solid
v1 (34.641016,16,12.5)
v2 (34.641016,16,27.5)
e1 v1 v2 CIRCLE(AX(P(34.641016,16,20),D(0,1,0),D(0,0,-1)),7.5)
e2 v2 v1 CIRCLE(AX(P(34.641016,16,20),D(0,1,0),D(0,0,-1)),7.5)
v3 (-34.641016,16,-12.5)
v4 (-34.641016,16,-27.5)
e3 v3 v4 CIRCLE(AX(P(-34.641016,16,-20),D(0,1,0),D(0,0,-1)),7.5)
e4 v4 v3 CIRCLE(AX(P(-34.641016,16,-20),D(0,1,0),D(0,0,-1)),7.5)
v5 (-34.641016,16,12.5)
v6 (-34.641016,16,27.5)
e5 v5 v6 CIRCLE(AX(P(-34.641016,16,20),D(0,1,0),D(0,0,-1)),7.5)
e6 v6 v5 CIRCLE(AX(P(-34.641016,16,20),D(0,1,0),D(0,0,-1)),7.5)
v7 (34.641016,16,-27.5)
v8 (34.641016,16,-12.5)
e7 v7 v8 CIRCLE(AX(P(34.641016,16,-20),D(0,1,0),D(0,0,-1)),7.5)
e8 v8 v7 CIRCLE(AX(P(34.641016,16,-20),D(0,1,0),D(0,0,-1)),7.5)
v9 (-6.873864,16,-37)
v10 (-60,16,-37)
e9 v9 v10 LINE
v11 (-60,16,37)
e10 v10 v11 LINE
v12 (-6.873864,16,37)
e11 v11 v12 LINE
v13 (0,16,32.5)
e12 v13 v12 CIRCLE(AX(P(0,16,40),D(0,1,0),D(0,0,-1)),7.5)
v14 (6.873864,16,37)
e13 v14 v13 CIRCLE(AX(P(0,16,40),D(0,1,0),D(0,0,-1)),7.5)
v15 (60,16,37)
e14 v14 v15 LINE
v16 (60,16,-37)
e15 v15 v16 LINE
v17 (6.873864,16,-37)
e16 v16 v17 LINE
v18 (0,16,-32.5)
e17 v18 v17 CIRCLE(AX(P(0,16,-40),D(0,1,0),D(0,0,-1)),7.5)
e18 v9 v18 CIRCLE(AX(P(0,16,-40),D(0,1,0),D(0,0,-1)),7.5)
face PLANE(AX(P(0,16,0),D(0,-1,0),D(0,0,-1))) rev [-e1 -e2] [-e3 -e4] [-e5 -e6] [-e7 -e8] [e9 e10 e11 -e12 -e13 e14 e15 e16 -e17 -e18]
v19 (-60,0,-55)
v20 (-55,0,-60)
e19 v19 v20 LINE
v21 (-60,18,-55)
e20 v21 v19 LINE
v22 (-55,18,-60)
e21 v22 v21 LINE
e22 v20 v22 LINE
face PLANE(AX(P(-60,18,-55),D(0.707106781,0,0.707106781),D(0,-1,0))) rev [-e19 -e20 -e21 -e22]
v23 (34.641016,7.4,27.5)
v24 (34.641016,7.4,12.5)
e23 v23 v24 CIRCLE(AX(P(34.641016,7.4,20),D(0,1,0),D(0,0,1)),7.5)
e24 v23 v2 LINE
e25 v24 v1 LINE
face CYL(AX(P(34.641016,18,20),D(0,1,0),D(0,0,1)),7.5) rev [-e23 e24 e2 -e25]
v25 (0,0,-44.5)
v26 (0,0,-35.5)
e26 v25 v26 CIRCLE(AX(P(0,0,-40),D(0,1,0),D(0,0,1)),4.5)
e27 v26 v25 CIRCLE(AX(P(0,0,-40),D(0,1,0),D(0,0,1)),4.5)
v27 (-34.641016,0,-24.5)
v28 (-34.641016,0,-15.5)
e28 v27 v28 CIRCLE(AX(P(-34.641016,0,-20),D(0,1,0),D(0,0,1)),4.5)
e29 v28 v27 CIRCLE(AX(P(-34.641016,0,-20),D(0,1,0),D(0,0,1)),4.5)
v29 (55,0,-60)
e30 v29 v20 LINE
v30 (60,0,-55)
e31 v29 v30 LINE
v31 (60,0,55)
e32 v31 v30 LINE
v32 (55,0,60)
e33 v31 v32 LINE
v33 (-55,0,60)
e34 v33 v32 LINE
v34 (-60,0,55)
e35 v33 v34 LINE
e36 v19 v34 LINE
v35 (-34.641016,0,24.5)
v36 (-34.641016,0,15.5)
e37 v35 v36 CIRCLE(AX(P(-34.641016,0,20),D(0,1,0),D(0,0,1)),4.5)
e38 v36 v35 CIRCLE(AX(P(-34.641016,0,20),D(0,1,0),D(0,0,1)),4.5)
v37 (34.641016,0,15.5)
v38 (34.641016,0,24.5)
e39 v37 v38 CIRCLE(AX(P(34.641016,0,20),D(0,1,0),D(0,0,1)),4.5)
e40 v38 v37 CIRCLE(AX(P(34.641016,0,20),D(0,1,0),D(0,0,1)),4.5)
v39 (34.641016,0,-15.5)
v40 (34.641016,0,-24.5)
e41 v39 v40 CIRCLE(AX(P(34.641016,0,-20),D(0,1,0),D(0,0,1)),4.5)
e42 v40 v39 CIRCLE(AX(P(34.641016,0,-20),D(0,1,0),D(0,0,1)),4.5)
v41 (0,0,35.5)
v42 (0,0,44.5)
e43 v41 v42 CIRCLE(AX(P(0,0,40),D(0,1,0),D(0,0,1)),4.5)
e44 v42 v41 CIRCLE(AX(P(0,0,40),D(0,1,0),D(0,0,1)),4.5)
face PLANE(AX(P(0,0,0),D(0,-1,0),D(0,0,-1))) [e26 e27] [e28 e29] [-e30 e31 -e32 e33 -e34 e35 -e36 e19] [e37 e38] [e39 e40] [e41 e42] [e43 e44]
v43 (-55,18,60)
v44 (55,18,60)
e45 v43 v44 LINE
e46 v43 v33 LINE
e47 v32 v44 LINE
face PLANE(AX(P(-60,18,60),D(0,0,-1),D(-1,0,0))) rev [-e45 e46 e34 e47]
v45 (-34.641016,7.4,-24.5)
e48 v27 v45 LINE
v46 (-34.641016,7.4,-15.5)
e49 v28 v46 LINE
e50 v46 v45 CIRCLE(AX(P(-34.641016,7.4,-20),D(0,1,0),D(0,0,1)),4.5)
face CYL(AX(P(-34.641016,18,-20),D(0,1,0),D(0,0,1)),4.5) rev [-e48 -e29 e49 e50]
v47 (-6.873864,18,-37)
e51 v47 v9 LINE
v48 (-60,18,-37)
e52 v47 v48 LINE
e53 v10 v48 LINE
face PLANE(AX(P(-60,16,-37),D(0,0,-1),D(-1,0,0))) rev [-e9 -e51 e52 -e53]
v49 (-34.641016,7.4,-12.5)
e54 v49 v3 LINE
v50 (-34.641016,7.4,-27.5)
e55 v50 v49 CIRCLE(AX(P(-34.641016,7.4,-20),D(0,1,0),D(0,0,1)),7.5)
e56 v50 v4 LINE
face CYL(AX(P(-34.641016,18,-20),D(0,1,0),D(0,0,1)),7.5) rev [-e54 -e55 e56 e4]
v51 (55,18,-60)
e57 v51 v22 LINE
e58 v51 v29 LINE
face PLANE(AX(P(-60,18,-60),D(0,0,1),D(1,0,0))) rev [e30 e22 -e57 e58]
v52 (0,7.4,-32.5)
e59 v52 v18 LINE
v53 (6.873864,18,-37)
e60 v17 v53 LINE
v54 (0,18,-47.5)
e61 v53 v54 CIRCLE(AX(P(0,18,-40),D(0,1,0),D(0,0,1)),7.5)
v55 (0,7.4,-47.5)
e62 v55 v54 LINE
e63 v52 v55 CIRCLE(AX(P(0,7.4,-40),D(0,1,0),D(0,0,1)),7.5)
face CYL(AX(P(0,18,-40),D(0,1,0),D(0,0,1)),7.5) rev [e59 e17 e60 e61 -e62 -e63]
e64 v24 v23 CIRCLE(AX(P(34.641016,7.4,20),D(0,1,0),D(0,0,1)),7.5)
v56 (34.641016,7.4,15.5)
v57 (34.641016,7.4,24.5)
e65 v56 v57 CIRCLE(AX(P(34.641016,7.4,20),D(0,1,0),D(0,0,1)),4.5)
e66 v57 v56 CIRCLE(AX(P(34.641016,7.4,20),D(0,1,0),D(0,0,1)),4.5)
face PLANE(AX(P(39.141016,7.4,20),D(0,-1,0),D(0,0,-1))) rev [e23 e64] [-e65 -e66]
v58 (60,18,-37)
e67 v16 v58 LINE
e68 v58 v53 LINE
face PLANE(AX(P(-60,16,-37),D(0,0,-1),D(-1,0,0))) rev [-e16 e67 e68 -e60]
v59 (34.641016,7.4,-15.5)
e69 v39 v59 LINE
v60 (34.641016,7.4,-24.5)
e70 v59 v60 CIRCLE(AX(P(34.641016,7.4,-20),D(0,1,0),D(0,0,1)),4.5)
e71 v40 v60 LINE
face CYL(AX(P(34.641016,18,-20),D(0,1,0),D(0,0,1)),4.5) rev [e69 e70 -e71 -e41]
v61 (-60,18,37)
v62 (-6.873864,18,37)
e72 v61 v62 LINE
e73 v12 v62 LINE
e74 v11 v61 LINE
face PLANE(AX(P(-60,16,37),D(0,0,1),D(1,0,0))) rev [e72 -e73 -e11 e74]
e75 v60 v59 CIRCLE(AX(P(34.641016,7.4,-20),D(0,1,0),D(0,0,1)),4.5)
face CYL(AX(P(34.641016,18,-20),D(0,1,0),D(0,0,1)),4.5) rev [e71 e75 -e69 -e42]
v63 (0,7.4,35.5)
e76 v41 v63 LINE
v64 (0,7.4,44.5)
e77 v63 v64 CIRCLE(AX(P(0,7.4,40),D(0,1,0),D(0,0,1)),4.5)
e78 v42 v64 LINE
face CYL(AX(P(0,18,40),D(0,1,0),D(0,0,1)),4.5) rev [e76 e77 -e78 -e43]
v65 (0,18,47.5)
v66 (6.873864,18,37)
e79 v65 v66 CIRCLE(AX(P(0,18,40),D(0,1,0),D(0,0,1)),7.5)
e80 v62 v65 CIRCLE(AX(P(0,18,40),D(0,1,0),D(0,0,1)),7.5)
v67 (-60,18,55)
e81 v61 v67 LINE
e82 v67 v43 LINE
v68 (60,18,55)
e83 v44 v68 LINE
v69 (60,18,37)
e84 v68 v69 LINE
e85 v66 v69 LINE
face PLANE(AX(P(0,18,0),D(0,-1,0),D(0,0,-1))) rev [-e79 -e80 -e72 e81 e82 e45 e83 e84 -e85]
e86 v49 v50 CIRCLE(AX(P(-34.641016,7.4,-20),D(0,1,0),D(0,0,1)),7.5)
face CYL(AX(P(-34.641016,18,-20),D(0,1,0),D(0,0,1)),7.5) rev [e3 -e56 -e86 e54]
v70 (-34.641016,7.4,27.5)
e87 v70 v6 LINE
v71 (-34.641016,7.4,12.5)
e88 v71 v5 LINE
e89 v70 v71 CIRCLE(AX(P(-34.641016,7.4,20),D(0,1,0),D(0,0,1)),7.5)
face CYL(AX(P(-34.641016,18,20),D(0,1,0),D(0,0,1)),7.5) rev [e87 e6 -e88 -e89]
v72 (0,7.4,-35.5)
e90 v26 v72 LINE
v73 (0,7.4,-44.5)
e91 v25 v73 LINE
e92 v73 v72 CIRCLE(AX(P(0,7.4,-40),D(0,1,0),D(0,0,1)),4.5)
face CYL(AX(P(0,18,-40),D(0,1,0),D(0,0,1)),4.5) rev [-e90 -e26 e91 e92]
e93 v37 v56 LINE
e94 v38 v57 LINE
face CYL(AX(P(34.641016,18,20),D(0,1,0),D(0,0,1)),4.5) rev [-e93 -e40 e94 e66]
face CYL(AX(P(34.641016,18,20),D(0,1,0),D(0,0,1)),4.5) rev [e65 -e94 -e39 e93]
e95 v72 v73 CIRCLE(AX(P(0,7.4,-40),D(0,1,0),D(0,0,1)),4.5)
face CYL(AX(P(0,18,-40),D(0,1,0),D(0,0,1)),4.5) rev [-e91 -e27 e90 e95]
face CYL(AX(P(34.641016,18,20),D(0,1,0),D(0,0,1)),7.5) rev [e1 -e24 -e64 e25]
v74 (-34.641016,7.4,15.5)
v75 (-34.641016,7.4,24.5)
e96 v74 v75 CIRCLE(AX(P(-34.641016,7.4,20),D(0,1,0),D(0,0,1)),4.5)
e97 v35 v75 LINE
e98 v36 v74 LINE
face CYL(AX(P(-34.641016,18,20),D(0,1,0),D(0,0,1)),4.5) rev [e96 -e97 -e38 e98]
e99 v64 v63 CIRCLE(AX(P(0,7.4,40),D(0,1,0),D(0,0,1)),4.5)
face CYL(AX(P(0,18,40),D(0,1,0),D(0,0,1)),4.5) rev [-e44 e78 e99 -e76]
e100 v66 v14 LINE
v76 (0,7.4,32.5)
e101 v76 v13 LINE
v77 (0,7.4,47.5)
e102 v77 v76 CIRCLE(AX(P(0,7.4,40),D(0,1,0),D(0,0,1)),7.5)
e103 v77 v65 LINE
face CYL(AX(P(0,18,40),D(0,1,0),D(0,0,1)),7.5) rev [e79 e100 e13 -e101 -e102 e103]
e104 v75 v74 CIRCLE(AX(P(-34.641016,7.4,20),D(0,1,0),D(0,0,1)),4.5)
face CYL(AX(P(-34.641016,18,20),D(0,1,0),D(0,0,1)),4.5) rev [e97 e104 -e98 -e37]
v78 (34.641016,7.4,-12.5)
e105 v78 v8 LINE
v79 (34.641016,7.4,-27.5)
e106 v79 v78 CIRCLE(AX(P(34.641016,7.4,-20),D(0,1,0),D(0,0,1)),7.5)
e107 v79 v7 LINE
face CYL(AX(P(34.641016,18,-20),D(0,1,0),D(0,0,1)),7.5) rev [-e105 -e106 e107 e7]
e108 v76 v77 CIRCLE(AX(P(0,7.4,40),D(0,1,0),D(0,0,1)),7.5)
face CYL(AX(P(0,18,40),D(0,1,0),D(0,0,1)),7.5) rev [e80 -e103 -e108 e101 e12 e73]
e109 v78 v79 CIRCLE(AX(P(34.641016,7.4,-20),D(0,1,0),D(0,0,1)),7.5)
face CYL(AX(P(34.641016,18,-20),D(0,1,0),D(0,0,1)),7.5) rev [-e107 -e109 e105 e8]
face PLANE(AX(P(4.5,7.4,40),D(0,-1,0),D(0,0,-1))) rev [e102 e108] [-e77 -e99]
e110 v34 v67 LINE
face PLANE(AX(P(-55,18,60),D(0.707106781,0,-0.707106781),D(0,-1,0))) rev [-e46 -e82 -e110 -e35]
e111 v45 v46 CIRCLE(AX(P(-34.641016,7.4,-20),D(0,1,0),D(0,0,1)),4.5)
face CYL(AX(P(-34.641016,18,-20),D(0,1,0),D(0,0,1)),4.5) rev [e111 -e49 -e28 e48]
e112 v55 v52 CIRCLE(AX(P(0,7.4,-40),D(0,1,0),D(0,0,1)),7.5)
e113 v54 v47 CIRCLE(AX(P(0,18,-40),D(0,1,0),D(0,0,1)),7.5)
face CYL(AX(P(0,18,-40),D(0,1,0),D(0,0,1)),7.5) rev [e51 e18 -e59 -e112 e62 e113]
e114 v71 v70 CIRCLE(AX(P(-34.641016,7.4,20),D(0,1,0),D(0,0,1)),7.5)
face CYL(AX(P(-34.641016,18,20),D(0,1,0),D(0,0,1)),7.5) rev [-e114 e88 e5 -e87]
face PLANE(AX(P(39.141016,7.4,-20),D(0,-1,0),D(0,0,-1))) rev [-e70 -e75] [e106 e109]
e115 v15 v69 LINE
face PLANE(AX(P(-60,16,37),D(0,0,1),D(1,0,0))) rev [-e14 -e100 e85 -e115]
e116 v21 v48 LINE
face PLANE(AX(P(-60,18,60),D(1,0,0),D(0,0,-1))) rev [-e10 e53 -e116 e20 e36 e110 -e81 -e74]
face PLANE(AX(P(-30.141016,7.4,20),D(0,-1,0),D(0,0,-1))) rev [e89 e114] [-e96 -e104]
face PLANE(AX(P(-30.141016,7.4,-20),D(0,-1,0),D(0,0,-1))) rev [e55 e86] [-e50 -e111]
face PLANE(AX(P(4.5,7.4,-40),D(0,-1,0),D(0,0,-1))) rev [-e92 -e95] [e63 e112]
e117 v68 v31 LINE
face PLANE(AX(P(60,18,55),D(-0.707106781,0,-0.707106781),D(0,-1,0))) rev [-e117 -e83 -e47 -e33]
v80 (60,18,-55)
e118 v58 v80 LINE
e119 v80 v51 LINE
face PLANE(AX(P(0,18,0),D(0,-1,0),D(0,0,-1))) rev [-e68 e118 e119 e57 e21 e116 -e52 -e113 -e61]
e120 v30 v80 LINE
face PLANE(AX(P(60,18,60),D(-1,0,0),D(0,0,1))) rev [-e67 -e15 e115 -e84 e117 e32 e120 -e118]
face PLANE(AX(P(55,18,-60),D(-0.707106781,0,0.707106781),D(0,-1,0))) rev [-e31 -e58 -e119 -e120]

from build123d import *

# Parameters (mm, degrees)
SKETCH_1_W                   = 120
SKETCH_1_H                   = 120
EXTRUDE_1_DEPTH              = 18
HOLE_WIZARD_M8_3_D           = 9
HOLE_WIZARD_M8_3_CBORE_D     = 15
HOLE_WIZARD_M8_3_CBORE_DEPTH = 10.6
SKETCH_11_W                  = 120
SKETCH_11_H                  = 74
CUT_EXTRUDE_2_DEPTH          = 2
CHAMFER_1_SIZE               = 5


with BuildPart() as part:
    # 草图1 → 凸台-拉伸1 (new body)
    with BuildSketch(Plane(origin=(0, 0, 0), x_dir=(1, 0, 0), z_dir=(0, 1, 0))):
        Rectangle(SKETCH_1_W, SKETCH_1_H)
    extrude(amount=EXTRUDE_1_DEPTH)

    # M8 六角凹头螺钉的柱形沉头孔3 (through all)
    with Locations(Plane(origin=(0, 18, 0), x_dir=(1, 0, 0), z_dir=(0, 1, 0))):
        with Locations((0, 40), (-34.641016151, 20), (-34.641016151, -20), (0, -40), (34.641016151, -20), (34.641016151, 20)):
            CounterBoreHole(HOLE_WIZARD_M8_3_D / 2, HOLE_WIZARD_M8_3_CBORE_D / 2, HOLE_WIZARD_M8_3_CBORE_DEPTH)

    # 草图11 → 切除-拉伸2 (cut)
    with BuildSketch(Plane(origin=(0, 18, 0), x_dir=(1, 0, 0), z_dir=(0, 1, 0))):
        Rectangle(SKETCH_11_W, SKETCH_11_H)
    extrude(amount=-CUT_EXTRUDE_2_DEPTH, mode=Mode.SUBTRACT)

    # 倒角1
    chamfer_1_edges = [part.edges().sort_by_distance(p)[0] for p in [
        (60, 9, 60),
        (-60, 9, 60),
        (-60, 9, -60),
        (60, 9, -60),
    ]]
    chamfer(chamfer_1_edges, length=CHAMFER_1_SIZE)


solid = part.part
